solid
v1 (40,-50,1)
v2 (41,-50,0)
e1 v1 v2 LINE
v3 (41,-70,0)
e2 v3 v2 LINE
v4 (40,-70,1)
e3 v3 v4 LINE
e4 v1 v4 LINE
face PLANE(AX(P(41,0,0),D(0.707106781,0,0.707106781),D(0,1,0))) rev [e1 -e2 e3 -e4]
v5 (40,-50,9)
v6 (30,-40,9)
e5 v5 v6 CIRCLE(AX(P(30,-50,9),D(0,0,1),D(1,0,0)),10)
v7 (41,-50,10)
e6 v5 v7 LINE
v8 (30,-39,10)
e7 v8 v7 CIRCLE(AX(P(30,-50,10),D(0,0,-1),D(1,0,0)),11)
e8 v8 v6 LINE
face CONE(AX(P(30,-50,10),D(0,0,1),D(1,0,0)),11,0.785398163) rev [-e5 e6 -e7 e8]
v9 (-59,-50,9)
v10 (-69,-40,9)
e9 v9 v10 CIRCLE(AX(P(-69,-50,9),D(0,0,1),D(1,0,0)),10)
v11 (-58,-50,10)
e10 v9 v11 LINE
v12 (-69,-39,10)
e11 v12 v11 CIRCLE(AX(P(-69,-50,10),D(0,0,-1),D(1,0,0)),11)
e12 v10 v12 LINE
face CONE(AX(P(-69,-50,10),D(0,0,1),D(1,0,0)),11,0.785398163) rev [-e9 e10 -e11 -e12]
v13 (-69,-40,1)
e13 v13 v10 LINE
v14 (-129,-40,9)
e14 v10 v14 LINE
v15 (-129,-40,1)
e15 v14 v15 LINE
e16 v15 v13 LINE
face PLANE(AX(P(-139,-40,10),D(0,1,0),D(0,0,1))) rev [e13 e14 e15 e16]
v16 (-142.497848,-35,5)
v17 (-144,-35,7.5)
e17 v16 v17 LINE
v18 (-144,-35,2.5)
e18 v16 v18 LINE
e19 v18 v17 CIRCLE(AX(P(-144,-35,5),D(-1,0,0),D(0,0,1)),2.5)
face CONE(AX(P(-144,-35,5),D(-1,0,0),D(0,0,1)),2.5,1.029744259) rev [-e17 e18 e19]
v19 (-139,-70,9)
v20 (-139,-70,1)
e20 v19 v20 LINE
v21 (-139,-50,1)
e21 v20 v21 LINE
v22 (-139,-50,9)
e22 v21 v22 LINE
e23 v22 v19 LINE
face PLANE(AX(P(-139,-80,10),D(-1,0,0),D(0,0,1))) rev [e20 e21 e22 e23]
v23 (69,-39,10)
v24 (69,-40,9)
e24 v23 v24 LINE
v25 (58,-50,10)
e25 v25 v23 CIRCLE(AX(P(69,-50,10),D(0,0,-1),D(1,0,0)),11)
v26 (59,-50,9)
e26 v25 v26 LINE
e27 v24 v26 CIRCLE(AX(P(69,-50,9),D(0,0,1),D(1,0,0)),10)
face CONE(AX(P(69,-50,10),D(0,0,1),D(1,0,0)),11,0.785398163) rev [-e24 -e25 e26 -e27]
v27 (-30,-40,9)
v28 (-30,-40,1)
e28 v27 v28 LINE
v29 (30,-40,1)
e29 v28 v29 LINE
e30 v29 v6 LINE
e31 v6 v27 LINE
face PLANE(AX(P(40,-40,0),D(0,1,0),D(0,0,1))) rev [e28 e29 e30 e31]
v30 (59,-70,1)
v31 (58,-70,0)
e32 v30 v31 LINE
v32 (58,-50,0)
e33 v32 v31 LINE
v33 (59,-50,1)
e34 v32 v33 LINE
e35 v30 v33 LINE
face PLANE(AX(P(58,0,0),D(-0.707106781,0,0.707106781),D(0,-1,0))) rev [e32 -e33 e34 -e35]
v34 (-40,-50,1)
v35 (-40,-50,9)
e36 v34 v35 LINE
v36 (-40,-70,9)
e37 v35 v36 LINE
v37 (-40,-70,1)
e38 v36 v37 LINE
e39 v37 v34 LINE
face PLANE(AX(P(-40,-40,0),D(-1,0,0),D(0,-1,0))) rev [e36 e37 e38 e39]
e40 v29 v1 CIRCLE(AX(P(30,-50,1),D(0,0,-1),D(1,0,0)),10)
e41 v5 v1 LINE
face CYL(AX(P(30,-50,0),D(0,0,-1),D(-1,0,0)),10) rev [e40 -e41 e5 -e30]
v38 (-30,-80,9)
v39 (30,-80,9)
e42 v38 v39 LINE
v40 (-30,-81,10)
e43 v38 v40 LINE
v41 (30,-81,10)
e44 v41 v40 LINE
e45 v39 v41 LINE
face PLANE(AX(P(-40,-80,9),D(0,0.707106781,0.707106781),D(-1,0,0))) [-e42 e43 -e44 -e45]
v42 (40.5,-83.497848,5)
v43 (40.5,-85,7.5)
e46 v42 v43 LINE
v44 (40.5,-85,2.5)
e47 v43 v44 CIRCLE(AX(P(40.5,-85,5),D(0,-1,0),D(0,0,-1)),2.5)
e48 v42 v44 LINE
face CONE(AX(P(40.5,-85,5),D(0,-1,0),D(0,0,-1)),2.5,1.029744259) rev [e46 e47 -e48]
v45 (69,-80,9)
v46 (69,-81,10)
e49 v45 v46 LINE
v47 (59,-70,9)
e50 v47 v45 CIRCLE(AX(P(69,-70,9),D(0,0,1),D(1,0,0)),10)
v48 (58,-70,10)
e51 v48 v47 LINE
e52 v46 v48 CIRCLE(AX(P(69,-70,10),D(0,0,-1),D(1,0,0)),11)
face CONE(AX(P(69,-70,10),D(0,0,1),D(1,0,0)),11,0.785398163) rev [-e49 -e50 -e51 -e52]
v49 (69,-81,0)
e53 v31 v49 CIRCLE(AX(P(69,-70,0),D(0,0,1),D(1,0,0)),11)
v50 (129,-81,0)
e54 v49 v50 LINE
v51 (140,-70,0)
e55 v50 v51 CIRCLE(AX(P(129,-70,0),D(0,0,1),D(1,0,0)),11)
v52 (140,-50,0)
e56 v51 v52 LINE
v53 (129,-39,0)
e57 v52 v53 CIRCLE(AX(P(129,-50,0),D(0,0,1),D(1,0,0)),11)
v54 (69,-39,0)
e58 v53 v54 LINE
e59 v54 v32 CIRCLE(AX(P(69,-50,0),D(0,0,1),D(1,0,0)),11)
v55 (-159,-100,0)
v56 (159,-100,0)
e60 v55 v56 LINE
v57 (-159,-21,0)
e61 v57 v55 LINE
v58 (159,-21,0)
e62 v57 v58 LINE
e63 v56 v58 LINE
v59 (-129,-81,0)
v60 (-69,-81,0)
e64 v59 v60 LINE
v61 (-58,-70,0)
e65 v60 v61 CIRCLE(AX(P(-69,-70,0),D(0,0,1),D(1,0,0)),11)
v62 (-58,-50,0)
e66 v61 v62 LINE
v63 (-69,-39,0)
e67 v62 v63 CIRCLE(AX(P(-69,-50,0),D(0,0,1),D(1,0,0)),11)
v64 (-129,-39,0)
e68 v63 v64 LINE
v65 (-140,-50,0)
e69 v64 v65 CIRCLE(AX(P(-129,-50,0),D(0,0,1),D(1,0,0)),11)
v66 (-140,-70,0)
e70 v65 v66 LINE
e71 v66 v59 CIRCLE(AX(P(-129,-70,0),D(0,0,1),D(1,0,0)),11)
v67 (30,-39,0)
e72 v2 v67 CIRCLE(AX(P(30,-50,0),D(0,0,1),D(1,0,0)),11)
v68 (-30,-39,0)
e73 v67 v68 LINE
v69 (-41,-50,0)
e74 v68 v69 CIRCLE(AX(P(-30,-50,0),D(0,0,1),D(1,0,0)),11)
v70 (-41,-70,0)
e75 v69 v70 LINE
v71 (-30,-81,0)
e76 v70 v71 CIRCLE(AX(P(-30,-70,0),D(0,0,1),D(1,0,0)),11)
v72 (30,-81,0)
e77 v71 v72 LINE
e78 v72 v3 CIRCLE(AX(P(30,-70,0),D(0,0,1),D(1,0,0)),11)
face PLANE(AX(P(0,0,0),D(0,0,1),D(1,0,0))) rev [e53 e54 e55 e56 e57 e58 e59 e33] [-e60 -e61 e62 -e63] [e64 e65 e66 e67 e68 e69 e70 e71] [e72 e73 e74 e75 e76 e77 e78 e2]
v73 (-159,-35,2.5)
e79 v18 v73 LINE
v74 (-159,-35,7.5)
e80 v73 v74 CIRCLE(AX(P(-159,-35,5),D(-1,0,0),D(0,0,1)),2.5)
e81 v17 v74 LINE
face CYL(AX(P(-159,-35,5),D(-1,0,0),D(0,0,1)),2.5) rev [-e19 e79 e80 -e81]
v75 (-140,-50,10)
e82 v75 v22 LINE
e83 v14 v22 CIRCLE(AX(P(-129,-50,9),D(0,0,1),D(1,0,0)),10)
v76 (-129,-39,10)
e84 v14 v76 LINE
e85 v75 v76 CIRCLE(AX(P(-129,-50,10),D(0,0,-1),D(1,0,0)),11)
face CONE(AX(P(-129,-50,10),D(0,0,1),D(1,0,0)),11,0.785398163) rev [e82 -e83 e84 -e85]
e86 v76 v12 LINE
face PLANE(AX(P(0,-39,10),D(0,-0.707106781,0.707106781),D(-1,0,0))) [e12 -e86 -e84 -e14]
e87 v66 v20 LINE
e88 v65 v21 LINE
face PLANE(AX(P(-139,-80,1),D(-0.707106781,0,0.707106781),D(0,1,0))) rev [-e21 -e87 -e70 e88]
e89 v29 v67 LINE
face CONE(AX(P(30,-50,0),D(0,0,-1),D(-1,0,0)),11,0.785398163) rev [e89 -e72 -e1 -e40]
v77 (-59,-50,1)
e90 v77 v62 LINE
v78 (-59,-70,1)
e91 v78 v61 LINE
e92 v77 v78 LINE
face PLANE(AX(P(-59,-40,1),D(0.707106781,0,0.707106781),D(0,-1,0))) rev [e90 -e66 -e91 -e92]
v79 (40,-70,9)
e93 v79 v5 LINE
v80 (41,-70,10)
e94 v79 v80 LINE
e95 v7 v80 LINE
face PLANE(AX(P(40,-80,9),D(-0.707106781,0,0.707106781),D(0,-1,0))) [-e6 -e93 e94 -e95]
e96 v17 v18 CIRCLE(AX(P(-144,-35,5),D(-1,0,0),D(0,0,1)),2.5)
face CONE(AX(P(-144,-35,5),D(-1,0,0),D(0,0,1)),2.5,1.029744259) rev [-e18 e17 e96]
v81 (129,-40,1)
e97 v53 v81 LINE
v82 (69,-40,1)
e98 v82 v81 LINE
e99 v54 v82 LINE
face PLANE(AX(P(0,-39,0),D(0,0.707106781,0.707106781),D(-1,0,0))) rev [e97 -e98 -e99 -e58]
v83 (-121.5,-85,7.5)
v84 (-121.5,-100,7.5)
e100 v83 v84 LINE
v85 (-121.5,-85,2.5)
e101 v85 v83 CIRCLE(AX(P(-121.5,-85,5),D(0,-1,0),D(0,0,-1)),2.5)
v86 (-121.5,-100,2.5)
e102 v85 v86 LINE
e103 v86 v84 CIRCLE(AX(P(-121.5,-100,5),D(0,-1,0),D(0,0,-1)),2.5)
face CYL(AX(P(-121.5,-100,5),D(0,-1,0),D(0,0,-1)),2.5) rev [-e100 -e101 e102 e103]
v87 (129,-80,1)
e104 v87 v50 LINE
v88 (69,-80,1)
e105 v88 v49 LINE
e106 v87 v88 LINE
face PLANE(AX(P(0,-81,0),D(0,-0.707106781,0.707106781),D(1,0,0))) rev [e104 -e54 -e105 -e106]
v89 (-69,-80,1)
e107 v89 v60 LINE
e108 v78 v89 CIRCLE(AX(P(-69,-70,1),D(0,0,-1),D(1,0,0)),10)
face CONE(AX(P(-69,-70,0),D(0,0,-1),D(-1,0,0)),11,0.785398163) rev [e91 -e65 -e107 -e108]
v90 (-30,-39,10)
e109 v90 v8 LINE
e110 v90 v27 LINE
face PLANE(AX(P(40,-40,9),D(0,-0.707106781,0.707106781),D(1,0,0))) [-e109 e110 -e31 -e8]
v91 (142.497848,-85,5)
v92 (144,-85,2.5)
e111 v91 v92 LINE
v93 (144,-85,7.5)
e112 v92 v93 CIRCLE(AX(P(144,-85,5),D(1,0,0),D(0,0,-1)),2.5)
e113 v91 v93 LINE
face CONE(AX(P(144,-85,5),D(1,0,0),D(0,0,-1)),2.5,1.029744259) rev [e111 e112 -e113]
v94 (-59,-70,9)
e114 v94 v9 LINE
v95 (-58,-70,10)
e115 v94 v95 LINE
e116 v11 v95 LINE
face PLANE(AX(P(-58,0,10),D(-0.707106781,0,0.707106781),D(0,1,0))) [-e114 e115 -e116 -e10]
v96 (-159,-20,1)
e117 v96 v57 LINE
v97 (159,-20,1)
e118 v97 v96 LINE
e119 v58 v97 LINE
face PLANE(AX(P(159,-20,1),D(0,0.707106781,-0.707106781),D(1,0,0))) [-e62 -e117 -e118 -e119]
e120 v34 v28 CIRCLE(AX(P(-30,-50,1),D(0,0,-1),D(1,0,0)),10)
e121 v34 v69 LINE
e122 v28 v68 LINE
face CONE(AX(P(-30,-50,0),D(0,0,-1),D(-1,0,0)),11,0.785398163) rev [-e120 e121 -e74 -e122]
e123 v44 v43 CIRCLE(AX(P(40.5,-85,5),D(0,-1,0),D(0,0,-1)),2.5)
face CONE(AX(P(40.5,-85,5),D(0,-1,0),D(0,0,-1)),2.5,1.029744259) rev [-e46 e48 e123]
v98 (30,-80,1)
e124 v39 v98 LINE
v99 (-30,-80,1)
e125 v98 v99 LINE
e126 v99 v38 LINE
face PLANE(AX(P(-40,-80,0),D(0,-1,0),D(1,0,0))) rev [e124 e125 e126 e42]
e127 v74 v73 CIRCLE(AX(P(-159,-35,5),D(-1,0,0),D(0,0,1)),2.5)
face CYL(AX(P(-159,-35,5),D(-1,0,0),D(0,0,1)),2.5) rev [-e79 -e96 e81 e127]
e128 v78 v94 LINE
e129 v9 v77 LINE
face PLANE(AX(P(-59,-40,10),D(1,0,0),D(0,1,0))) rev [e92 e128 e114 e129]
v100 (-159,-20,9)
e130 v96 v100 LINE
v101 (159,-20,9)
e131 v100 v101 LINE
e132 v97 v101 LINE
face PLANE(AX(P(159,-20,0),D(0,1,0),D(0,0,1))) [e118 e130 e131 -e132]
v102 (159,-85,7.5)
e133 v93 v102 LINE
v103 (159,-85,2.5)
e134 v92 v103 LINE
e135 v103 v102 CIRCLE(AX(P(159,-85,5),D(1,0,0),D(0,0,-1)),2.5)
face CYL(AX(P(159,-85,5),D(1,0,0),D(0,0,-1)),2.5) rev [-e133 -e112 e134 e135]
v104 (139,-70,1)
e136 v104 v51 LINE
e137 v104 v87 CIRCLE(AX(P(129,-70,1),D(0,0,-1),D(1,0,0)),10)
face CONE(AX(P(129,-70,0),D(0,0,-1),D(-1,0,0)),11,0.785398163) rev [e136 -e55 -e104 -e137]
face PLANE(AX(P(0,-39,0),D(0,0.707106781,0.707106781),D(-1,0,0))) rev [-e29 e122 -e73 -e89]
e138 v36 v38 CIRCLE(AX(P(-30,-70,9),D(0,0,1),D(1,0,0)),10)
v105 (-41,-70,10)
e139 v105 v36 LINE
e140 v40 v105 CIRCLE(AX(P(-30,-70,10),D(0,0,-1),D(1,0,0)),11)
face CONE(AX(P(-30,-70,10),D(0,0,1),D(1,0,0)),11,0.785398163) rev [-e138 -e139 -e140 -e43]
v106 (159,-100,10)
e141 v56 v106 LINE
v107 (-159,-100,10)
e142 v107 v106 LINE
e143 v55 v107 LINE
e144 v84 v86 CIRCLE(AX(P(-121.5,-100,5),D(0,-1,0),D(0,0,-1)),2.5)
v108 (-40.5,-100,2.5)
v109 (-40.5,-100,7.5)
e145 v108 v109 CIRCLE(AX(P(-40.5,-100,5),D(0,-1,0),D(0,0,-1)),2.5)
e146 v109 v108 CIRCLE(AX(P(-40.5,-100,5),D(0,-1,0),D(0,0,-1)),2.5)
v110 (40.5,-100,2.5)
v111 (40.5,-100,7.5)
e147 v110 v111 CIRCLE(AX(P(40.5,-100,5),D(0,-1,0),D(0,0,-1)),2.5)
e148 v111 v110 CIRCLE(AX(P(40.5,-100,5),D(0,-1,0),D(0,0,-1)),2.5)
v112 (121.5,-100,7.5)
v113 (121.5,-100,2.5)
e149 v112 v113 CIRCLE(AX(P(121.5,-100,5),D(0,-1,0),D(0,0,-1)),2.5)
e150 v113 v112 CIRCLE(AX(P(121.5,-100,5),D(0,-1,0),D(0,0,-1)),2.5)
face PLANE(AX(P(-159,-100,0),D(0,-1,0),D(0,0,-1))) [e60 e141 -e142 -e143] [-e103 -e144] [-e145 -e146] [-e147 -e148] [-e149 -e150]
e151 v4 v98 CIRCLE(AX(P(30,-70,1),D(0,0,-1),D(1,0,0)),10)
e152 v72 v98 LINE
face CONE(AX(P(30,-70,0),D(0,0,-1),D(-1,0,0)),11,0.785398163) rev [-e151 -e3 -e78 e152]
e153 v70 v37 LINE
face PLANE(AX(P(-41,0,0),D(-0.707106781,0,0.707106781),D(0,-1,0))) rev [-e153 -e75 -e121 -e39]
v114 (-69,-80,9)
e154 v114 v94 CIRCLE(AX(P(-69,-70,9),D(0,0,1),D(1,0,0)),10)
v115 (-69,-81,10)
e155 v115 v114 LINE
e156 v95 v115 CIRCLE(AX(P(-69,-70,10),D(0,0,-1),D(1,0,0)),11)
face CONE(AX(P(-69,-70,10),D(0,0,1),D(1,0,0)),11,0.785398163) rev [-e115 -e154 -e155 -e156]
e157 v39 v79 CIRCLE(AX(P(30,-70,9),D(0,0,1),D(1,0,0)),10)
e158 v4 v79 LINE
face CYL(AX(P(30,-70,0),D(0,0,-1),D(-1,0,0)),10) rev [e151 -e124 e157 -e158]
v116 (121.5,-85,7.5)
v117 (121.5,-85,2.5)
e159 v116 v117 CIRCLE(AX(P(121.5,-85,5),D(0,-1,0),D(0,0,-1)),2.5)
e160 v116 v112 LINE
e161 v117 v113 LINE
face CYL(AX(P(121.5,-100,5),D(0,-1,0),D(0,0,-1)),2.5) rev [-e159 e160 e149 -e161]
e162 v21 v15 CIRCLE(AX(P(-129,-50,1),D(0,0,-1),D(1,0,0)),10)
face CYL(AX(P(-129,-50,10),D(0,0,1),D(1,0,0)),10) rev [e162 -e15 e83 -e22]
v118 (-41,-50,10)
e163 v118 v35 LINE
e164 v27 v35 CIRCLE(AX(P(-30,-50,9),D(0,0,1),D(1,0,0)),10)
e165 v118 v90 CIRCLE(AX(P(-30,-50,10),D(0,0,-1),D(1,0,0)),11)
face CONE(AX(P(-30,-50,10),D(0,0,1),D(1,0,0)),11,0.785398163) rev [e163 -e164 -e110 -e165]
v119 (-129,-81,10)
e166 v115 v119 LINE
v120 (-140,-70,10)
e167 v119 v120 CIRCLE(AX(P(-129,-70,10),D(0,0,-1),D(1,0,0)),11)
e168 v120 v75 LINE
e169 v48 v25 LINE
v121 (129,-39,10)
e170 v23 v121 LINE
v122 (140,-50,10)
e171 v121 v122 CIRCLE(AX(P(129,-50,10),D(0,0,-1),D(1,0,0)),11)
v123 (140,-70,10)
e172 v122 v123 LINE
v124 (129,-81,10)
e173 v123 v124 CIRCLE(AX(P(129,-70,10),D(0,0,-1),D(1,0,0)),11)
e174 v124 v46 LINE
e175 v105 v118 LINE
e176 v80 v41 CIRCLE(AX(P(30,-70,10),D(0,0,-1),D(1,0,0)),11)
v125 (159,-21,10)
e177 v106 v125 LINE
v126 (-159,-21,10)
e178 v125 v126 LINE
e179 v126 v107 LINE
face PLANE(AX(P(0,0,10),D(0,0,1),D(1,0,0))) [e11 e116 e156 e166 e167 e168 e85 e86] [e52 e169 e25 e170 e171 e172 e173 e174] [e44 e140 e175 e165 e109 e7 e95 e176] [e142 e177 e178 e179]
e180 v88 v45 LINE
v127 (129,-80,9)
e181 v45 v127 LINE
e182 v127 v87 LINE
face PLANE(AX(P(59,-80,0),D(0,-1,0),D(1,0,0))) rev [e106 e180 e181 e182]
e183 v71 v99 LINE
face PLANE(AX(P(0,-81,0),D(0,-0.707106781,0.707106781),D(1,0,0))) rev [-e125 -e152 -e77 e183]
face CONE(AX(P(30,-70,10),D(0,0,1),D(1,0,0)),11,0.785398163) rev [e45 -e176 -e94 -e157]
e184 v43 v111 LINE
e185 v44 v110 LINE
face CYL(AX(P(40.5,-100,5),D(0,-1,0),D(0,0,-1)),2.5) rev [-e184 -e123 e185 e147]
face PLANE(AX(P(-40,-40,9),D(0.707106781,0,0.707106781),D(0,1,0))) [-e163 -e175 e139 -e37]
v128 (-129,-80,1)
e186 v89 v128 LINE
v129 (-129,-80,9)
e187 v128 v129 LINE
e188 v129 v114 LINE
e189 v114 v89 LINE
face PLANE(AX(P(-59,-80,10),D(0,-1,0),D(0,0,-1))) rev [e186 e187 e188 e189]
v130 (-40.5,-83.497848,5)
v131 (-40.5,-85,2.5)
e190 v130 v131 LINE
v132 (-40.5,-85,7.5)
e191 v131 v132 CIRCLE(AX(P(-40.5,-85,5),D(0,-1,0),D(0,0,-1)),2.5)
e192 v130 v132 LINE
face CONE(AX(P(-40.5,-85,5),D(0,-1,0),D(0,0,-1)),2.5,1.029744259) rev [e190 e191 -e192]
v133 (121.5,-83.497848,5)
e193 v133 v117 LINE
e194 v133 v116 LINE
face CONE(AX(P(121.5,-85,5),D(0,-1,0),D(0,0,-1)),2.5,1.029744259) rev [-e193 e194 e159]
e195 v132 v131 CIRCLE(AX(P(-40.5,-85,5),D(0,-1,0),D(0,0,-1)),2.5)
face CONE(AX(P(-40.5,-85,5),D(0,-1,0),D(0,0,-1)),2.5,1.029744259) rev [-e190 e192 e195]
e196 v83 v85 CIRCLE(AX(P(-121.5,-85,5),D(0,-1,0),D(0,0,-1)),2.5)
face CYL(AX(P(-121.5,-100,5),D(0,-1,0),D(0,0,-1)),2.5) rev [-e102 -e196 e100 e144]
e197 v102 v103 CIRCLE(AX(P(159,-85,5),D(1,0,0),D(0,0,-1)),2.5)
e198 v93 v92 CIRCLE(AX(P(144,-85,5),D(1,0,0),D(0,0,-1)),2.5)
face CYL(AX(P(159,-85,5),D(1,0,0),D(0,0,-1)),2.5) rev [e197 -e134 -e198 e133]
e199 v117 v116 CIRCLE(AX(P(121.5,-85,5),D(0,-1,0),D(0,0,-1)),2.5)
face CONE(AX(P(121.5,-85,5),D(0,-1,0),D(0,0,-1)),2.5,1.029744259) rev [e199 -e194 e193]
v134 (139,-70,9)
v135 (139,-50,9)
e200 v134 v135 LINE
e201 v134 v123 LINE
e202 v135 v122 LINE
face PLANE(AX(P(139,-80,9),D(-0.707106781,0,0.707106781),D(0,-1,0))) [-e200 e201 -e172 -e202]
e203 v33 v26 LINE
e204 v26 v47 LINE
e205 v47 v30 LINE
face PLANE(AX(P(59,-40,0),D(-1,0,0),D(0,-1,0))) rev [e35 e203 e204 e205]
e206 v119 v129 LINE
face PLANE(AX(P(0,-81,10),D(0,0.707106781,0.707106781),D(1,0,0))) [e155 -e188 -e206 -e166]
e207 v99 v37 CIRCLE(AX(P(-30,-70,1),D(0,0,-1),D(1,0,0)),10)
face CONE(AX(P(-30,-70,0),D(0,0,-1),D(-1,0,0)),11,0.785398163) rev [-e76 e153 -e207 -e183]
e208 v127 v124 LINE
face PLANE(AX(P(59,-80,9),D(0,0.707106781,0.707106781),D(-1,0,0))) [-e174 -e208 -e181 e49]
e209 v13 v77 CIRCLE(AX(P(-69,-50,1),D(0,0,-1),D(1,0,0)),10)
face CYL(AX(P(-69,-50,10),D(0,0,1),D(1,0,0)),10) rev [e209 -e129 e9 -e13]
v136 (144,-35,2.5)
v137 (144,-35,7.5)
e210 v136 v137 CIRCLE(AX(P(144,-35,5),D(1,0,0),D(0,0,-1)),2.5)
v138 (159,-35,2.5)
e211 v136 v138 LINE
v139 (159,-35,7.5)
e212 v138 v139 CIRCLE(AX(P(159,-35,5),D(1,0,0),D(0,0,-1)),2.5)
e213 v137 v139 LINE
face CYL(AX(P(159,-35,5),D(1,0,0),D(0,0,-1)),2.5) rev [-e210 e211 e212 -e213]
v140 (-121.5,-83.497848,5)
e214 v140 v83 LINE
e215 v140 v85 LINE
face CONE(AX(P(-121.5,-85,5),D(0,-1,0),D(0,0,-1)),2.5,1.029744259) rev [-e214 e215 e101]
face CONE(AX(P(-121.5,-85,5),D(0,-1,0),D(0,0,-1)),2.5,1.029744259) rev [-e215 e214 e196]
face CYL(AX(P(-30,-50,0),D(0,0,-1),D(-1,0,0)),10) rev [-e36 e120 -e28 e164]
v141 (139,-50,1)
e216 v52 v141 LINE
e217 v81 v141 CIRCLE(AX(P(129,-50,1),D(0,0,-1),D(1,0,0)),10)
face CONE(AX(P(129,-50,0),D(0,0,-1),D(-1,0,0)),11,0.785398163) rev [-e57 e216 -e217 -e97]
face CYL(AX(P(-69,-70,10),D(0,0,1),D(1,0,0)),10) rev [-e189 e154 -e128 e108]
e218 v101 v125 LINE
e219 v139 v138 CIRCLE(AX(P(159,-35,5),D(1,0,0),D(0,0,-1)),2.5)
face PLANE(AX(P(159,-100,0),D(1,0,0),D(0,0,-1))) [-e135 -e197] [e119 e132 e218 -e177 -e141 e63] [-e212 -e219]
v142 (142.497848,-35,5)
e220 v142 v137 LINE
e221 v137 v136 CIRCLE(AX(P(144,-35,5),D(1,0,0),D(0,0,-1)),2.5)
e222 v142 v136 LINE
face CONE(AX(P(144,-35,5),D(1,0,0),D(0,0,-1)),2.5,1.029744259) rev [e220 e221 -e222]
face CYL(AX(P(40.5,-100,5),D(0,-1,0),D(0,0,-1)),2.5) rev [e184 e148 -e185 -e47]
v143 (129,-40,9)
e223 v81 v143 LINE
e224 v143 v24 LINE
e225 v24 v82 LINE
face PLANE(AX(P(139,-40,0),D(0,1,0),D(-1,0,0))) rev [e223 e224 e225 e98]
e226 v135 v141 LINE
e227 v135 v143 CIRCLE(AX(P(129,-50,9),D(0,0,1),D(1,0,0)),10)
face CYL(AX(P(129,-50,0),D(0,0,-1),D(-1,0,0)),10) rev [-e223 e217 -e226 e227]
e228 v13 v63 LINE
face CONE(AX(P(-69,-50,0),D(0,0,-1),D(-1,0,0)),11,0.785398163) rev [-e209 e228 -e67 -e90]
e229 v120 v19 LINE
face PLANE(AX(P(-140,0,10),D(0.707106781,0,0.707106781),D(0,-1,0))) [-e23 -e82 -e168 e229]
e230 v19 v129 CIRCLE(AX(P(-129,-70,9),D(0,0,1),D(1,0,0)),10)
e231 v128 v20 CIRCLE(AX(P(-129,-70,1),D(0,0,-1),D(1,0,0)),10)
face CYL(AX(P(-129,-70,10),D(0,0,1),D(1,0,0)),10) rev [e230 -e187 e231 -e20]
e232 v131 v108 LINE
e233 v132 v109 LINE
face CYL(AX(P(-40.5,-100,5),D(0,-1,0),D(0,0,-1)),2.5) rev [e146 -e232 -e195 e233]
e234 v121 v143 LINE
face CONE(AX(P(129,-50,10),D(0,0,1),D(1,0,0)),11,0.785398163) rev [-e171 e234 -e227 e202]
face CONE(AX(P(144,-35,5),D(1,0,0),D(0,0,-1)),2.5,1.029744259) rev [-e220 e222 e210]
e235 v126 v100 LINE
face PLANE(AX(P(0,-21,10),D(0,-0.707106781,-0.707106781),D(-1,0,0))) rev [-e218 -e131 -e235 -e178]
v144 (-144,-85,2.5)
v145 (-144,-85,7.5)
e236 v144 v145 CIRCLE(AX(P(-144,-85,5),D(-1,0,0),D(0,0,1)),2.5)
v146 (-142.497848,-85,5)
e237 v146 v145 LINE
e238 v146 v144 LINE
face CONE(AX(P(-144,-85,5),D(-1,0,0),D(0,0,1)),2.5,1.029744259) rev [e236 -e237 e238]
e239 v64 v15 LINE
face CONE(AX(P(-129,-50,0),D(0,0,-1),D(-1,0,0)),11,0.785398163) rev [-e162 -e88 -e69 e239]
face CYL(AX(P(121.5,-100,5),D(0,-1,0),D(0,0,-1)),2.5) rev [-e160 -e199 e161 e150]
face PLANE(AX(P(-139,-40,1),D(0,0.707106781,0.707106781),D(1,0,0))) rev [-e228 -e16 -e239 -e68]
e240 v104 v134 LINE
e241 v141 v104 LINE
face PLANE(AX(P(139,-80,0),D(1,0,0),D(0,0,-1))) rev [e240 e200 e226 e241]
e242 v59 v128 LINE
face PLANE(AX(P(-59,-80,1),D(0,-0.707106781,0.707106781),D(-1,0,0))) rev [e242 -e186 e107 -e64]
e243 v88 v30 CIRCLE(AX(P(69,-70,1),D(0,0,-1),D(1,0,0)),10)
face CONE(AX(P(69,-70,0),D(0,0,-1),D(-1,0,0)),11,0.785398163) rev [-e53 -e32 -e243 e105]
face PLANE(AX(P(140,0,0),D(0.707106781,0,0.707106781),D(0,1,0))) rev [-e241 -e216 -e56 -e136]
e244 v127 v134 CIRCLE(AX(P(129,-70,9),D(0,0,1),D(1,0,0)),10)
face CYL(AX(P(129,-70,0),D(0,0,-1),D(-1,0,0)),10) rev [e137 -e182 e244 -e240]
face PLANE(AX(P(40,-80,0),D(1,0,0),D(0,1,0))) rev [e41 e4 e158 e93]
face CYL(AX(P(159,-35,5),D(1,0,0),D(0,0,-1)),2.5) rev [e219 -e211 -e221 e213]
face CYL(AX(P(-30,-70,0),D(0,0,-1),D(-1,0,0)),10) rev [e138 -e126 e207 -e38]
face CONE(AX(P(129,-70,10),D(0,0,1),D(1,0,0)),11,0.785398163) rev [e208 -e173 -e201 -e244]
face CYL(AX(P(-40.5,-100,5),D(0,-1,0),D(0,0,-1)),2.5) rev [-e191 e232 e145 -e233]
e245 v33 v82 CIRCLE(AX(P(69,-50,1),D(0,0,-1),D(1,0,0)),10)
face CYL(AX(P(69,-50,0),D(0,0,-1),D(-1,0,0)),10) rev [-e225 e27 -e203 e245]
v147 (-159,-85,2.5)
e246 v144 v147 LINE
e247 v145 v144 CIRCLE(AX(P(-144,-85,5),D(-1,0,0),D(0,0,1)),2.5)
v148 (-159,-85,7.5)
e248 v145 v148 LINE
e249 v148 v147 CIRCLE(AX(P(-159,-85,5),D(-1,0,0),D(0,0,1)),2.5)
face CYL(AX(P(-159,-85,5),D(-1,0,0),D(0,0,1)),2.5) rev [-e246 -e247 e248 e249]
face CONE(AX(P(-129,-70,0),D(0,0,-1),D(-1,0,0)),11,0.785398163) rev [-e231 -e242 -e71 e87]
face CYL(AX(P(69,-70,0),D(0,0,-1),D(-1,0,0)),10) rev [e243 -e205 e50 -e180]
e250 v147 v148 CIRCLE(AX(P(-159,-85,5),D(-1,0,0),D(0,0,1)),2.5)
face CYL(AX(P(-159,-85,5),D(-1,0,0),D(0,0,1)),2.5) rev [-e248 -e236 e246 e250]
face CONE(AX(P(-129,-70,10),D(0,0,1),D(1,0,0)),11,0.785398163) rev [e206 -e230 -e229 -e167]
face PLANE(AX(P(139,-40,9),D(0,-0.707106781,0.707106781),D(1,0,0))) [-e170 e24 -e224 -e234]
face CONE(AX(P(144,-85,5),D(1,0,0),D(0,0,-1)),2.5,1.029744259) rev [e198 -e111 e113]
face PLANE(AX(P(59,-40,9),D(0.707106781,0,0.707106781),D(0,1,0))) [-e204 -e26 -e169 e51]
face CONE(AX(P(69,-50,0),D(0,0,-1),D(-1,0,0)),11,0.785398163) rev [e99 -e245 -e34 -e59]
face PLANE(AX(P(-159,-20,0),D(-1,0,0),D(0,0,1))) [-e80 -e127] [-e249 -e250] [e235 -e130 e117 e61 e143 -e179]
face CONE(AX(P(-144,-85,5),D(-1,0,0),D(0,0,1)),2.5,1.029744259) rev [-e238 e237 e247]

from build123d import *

# Parameters (mm, degrees)
SKETCH_1_W                = 318
SKETCH_1_H                = 80
EXTRUDE_1_DEPTH           = 10
SKETCH_2_W                = 80
SKETCH_2_H                = 40
CUT_EXTRUDE_1_DEPTH       = 189.098378515
SKETCH_3_W                = 80
SKETCH_3_H                = 40
CUT_EXTRUDE_2_DEPTH       = 189.098378515
SKETCH_4_W                = 80
SKETCH_4_H                = 40
CUT_EXTRUDE_3_DEPTH       = 189.098378515
HOLE_WIZARD_5_0_5_1_D     = 5
HOLE_WIZARD_5_0_5_1_DEPTH = 15
HOLE_WIZARD_5_0_5_1_TIP   = 1.502151548
HOLE_WIZARD_5_0_5_2_D     = 5
HOLE_WIZARD_5_0_5_2_DEPTH = 15
HOLE_WIZARD_5_0_5_2_TIP   = 1.502151548
HOLE_WIZARD_5_0_5_3_D     = 5
HOLE_WIZARD_5_0_5_3_DEPTH = 15
HOLE_WIZARD_5_0_5_3_TIP   = 1.502151548
FILLET_1_R                = 10
CHAMFER_1_SIZE            = 1


with BuildPart() as part:
    # 草图1 → 凸台-拉伸1 (new body)
    with BuildSketch(Plane.XY.offset(10)):
        with Locations((0, -60)):
            Rectangle(SKETCH_1_W, SKETCH_1_H)
    extrude(amount=-EXTRUDE_1_DEPTH)

    # 草图2 → 切除-拉伸1 (cut, through all)
    with BuildSketch(Plane.XY.offset(10)):
        with Locations((0, -60)):
            Rectangle(SKETCH_2_W, SKETCH_2_H)
    extrude(amount=-CUT_EXTRUDE_1_DEPTH, mode=Mode.SUBTRACT)

    # 草图3 → 切除-拉伸2 (cut, through all)
    with BuildSketch(Plane.XY.offset(10)):
        with Locations((99, -60)):
            Rectangle(SKETCH_3_W, SKETCH_3_H)
    extrude(amount=-CUT_EXTRUDE_2_DEPTH, mode=Mode.SUBTRACT)

    # 草图4 → 切除-拉伸3 (cut, through all)
    with BuildSketch(Plane(origin=(0, 0, 0), x_dir=(-1, 0, 0), z_dir=(0, 0, -1))):
        with Locations((99, -60)):
            Rectangle(SKETCH_4_W, SKETCH_4_H)
    extrude(amount=-CUT_EXTRUDE_3_DEPTH, mode=Mode.SUBTRACT)

    # Ø5.0 (5) 直径孔1
    with Locations(Plane.ZY.offset(159)):
        with Locations((5, -35), (5, -85)):
            Hole(HOLE_WIZARD_5_0_5_1_D / 2, depth=HOLE_WIZARD_5_0_5_1_DEPTH)
            with Locations((0, 0, -(HOLE_WIZARD_5_0_5_1_DEPTH + HOLE_WIZARD_5_0_5_1_TIP / 2))):  # 118° drill point
                Cone(0, HOLE_WIZARD_5_0_5_1_D / 2, HOLE_WIZARD_5_0_5_1_TIP, mode=Mode.SUBTRACT)

    # Ø5.0 (5) 直径孔2
    with Locations(Plane(origin=(159, 0, 0), x_dir=(0, 0, -1), z_dir=(1, 0, 0))):
        with Locations((-5, -35), (-5, -85)):
            Hole(HOLE_WIZARD_5_0_5_2_D / 2, depth=HOLE_WIZARD_5_0_5_2_DEPTH)
            with Locations((0, 0, -(HOLE_WIZARD_5_0_5_2_DEPTH + HOLE_WIZARD_5_0_5_2_TIP / 2))):  # 118° drill point
                Cone(0, HOLE_WIZARD_5_0_5_2_D / 2, HOLE_WIZARD_5_0_5_2_TIP, mode=Mode.SUBTRACT)

    # Ø5.0 (5) 直径孔3
    with Locations(Plane(origin=(0, -100, 0), x_dir=(-1, 0, 0), z_dir=(0, -1, 0))):
        with Locations((121.5, -5), (40.5, -5), (-40.5, -5), (-121.5, -5)):
            Hole(HOLE_WIZARD_5_0_5_3_D / 2, depth=HOLE_WIZARD_5_0_5_3_DEPTH)
            with Locations((0, 0, -(HOLE_WIZARD_5_0_5_3_DEPTH + HOLE_WIZARD_5_0_5_3_TIP / 2))):  # 118° drill point
                Cone(0, HOLE_WIZARD_5_0_5_3_D / 2, HOLE_WIZARD_5_0_5_3_TIP, mode=Mode.SUBTRACT)

    # 圆角1
    fillet_1_edges = [part.edges().sort_by_distance(p)[0] for p in [
        (40, -80, 5),
        (-40, -80, 5),
        (-40, -40, 5),
        (40, -40, 5),
        (139, -80, 5),
        (59, -80, 5),
        (59, -40, 5),
        (139, -40, 5),
        (-59, -40, 5),
        (-139, -40, 5),
        (-139, -80, 5),
        (-59, -80, 5),
    ]]
    fillet(fillet_1_edges, radius=FILLET_1_R)

    # 倒角1
    chamfer_1_edges = [part.edges().sort_by_distance(p)[0] for p in [
        (0, -40, 10),
        (0, -40, 0),
        (40, -60, 10),
        (40, -60, 0),
        (99, -40, 10),
        (99, -40, 0),
        (139, -60, 10),
        (139, -60, 0),
        (0, -80, 10),
        (0, -80, 0),
        (-40, -60, 10),
        (-40, -60, 0),
        (99, -80, 10),
        (99, -80, 0),
        (-99, -40, 0),
        (-99, -40, 10),
        (-139, -60, 0),
        (-139, -60, 10),
        (59, -60, 10),
        (59, -60, 0),
        (-59, -60, 0),
        (-59, -60, 10),
        (-99, -80, 0),
        (-99, -80, 10),
        (37.071067812, -42.928932188, 10),
        (37.071067812, -42.928932188, 0),
        (136.071067812, -42.928932188, 10),
        (136.071067812, -42.928932188, 0),
        (-37.071067812, -77.071067812, 10),
        (-37.071067812, -77.071067812, 0),
        (136.071067812, -77.071067812, 10),
        (136.071067812, -77.071067812, 0),
        (-136.071067812, -42.928932188, 0),
        (-136.071067812, -42.928932188, 10),
        (61.928932188, -42.928932188, 10),
        (61.928932188, -42.928932188, 0),
        (37.071067812, -77.071067812, 10),
        (37.071067812, -77.071067812, 0),
        (-61.928932188, -42.928932188, 0),
        (-61.928932188, -42.928932188, 10),
        (-37.071067812, -42.928932188, 10),
        (-37.071067812, -42.928932188, 0),
        (-61.928932188, -77.071067812, 0),
        (-61.928932188, -77.071067812, 10),
        (-136.071067812, -77.071067812, 0),
        (-136.071067812, -77.071067812, 10),
        (61.928932188, -77.071067812, 10),
        (61.928932188, -77.071067812, 0),
        (0, -20, 0),
        (0, -20, 10),
    ]]
    chamfer(chamfer_1_edges, length=CHAMFER_1_SIZE)


solid = part.part
